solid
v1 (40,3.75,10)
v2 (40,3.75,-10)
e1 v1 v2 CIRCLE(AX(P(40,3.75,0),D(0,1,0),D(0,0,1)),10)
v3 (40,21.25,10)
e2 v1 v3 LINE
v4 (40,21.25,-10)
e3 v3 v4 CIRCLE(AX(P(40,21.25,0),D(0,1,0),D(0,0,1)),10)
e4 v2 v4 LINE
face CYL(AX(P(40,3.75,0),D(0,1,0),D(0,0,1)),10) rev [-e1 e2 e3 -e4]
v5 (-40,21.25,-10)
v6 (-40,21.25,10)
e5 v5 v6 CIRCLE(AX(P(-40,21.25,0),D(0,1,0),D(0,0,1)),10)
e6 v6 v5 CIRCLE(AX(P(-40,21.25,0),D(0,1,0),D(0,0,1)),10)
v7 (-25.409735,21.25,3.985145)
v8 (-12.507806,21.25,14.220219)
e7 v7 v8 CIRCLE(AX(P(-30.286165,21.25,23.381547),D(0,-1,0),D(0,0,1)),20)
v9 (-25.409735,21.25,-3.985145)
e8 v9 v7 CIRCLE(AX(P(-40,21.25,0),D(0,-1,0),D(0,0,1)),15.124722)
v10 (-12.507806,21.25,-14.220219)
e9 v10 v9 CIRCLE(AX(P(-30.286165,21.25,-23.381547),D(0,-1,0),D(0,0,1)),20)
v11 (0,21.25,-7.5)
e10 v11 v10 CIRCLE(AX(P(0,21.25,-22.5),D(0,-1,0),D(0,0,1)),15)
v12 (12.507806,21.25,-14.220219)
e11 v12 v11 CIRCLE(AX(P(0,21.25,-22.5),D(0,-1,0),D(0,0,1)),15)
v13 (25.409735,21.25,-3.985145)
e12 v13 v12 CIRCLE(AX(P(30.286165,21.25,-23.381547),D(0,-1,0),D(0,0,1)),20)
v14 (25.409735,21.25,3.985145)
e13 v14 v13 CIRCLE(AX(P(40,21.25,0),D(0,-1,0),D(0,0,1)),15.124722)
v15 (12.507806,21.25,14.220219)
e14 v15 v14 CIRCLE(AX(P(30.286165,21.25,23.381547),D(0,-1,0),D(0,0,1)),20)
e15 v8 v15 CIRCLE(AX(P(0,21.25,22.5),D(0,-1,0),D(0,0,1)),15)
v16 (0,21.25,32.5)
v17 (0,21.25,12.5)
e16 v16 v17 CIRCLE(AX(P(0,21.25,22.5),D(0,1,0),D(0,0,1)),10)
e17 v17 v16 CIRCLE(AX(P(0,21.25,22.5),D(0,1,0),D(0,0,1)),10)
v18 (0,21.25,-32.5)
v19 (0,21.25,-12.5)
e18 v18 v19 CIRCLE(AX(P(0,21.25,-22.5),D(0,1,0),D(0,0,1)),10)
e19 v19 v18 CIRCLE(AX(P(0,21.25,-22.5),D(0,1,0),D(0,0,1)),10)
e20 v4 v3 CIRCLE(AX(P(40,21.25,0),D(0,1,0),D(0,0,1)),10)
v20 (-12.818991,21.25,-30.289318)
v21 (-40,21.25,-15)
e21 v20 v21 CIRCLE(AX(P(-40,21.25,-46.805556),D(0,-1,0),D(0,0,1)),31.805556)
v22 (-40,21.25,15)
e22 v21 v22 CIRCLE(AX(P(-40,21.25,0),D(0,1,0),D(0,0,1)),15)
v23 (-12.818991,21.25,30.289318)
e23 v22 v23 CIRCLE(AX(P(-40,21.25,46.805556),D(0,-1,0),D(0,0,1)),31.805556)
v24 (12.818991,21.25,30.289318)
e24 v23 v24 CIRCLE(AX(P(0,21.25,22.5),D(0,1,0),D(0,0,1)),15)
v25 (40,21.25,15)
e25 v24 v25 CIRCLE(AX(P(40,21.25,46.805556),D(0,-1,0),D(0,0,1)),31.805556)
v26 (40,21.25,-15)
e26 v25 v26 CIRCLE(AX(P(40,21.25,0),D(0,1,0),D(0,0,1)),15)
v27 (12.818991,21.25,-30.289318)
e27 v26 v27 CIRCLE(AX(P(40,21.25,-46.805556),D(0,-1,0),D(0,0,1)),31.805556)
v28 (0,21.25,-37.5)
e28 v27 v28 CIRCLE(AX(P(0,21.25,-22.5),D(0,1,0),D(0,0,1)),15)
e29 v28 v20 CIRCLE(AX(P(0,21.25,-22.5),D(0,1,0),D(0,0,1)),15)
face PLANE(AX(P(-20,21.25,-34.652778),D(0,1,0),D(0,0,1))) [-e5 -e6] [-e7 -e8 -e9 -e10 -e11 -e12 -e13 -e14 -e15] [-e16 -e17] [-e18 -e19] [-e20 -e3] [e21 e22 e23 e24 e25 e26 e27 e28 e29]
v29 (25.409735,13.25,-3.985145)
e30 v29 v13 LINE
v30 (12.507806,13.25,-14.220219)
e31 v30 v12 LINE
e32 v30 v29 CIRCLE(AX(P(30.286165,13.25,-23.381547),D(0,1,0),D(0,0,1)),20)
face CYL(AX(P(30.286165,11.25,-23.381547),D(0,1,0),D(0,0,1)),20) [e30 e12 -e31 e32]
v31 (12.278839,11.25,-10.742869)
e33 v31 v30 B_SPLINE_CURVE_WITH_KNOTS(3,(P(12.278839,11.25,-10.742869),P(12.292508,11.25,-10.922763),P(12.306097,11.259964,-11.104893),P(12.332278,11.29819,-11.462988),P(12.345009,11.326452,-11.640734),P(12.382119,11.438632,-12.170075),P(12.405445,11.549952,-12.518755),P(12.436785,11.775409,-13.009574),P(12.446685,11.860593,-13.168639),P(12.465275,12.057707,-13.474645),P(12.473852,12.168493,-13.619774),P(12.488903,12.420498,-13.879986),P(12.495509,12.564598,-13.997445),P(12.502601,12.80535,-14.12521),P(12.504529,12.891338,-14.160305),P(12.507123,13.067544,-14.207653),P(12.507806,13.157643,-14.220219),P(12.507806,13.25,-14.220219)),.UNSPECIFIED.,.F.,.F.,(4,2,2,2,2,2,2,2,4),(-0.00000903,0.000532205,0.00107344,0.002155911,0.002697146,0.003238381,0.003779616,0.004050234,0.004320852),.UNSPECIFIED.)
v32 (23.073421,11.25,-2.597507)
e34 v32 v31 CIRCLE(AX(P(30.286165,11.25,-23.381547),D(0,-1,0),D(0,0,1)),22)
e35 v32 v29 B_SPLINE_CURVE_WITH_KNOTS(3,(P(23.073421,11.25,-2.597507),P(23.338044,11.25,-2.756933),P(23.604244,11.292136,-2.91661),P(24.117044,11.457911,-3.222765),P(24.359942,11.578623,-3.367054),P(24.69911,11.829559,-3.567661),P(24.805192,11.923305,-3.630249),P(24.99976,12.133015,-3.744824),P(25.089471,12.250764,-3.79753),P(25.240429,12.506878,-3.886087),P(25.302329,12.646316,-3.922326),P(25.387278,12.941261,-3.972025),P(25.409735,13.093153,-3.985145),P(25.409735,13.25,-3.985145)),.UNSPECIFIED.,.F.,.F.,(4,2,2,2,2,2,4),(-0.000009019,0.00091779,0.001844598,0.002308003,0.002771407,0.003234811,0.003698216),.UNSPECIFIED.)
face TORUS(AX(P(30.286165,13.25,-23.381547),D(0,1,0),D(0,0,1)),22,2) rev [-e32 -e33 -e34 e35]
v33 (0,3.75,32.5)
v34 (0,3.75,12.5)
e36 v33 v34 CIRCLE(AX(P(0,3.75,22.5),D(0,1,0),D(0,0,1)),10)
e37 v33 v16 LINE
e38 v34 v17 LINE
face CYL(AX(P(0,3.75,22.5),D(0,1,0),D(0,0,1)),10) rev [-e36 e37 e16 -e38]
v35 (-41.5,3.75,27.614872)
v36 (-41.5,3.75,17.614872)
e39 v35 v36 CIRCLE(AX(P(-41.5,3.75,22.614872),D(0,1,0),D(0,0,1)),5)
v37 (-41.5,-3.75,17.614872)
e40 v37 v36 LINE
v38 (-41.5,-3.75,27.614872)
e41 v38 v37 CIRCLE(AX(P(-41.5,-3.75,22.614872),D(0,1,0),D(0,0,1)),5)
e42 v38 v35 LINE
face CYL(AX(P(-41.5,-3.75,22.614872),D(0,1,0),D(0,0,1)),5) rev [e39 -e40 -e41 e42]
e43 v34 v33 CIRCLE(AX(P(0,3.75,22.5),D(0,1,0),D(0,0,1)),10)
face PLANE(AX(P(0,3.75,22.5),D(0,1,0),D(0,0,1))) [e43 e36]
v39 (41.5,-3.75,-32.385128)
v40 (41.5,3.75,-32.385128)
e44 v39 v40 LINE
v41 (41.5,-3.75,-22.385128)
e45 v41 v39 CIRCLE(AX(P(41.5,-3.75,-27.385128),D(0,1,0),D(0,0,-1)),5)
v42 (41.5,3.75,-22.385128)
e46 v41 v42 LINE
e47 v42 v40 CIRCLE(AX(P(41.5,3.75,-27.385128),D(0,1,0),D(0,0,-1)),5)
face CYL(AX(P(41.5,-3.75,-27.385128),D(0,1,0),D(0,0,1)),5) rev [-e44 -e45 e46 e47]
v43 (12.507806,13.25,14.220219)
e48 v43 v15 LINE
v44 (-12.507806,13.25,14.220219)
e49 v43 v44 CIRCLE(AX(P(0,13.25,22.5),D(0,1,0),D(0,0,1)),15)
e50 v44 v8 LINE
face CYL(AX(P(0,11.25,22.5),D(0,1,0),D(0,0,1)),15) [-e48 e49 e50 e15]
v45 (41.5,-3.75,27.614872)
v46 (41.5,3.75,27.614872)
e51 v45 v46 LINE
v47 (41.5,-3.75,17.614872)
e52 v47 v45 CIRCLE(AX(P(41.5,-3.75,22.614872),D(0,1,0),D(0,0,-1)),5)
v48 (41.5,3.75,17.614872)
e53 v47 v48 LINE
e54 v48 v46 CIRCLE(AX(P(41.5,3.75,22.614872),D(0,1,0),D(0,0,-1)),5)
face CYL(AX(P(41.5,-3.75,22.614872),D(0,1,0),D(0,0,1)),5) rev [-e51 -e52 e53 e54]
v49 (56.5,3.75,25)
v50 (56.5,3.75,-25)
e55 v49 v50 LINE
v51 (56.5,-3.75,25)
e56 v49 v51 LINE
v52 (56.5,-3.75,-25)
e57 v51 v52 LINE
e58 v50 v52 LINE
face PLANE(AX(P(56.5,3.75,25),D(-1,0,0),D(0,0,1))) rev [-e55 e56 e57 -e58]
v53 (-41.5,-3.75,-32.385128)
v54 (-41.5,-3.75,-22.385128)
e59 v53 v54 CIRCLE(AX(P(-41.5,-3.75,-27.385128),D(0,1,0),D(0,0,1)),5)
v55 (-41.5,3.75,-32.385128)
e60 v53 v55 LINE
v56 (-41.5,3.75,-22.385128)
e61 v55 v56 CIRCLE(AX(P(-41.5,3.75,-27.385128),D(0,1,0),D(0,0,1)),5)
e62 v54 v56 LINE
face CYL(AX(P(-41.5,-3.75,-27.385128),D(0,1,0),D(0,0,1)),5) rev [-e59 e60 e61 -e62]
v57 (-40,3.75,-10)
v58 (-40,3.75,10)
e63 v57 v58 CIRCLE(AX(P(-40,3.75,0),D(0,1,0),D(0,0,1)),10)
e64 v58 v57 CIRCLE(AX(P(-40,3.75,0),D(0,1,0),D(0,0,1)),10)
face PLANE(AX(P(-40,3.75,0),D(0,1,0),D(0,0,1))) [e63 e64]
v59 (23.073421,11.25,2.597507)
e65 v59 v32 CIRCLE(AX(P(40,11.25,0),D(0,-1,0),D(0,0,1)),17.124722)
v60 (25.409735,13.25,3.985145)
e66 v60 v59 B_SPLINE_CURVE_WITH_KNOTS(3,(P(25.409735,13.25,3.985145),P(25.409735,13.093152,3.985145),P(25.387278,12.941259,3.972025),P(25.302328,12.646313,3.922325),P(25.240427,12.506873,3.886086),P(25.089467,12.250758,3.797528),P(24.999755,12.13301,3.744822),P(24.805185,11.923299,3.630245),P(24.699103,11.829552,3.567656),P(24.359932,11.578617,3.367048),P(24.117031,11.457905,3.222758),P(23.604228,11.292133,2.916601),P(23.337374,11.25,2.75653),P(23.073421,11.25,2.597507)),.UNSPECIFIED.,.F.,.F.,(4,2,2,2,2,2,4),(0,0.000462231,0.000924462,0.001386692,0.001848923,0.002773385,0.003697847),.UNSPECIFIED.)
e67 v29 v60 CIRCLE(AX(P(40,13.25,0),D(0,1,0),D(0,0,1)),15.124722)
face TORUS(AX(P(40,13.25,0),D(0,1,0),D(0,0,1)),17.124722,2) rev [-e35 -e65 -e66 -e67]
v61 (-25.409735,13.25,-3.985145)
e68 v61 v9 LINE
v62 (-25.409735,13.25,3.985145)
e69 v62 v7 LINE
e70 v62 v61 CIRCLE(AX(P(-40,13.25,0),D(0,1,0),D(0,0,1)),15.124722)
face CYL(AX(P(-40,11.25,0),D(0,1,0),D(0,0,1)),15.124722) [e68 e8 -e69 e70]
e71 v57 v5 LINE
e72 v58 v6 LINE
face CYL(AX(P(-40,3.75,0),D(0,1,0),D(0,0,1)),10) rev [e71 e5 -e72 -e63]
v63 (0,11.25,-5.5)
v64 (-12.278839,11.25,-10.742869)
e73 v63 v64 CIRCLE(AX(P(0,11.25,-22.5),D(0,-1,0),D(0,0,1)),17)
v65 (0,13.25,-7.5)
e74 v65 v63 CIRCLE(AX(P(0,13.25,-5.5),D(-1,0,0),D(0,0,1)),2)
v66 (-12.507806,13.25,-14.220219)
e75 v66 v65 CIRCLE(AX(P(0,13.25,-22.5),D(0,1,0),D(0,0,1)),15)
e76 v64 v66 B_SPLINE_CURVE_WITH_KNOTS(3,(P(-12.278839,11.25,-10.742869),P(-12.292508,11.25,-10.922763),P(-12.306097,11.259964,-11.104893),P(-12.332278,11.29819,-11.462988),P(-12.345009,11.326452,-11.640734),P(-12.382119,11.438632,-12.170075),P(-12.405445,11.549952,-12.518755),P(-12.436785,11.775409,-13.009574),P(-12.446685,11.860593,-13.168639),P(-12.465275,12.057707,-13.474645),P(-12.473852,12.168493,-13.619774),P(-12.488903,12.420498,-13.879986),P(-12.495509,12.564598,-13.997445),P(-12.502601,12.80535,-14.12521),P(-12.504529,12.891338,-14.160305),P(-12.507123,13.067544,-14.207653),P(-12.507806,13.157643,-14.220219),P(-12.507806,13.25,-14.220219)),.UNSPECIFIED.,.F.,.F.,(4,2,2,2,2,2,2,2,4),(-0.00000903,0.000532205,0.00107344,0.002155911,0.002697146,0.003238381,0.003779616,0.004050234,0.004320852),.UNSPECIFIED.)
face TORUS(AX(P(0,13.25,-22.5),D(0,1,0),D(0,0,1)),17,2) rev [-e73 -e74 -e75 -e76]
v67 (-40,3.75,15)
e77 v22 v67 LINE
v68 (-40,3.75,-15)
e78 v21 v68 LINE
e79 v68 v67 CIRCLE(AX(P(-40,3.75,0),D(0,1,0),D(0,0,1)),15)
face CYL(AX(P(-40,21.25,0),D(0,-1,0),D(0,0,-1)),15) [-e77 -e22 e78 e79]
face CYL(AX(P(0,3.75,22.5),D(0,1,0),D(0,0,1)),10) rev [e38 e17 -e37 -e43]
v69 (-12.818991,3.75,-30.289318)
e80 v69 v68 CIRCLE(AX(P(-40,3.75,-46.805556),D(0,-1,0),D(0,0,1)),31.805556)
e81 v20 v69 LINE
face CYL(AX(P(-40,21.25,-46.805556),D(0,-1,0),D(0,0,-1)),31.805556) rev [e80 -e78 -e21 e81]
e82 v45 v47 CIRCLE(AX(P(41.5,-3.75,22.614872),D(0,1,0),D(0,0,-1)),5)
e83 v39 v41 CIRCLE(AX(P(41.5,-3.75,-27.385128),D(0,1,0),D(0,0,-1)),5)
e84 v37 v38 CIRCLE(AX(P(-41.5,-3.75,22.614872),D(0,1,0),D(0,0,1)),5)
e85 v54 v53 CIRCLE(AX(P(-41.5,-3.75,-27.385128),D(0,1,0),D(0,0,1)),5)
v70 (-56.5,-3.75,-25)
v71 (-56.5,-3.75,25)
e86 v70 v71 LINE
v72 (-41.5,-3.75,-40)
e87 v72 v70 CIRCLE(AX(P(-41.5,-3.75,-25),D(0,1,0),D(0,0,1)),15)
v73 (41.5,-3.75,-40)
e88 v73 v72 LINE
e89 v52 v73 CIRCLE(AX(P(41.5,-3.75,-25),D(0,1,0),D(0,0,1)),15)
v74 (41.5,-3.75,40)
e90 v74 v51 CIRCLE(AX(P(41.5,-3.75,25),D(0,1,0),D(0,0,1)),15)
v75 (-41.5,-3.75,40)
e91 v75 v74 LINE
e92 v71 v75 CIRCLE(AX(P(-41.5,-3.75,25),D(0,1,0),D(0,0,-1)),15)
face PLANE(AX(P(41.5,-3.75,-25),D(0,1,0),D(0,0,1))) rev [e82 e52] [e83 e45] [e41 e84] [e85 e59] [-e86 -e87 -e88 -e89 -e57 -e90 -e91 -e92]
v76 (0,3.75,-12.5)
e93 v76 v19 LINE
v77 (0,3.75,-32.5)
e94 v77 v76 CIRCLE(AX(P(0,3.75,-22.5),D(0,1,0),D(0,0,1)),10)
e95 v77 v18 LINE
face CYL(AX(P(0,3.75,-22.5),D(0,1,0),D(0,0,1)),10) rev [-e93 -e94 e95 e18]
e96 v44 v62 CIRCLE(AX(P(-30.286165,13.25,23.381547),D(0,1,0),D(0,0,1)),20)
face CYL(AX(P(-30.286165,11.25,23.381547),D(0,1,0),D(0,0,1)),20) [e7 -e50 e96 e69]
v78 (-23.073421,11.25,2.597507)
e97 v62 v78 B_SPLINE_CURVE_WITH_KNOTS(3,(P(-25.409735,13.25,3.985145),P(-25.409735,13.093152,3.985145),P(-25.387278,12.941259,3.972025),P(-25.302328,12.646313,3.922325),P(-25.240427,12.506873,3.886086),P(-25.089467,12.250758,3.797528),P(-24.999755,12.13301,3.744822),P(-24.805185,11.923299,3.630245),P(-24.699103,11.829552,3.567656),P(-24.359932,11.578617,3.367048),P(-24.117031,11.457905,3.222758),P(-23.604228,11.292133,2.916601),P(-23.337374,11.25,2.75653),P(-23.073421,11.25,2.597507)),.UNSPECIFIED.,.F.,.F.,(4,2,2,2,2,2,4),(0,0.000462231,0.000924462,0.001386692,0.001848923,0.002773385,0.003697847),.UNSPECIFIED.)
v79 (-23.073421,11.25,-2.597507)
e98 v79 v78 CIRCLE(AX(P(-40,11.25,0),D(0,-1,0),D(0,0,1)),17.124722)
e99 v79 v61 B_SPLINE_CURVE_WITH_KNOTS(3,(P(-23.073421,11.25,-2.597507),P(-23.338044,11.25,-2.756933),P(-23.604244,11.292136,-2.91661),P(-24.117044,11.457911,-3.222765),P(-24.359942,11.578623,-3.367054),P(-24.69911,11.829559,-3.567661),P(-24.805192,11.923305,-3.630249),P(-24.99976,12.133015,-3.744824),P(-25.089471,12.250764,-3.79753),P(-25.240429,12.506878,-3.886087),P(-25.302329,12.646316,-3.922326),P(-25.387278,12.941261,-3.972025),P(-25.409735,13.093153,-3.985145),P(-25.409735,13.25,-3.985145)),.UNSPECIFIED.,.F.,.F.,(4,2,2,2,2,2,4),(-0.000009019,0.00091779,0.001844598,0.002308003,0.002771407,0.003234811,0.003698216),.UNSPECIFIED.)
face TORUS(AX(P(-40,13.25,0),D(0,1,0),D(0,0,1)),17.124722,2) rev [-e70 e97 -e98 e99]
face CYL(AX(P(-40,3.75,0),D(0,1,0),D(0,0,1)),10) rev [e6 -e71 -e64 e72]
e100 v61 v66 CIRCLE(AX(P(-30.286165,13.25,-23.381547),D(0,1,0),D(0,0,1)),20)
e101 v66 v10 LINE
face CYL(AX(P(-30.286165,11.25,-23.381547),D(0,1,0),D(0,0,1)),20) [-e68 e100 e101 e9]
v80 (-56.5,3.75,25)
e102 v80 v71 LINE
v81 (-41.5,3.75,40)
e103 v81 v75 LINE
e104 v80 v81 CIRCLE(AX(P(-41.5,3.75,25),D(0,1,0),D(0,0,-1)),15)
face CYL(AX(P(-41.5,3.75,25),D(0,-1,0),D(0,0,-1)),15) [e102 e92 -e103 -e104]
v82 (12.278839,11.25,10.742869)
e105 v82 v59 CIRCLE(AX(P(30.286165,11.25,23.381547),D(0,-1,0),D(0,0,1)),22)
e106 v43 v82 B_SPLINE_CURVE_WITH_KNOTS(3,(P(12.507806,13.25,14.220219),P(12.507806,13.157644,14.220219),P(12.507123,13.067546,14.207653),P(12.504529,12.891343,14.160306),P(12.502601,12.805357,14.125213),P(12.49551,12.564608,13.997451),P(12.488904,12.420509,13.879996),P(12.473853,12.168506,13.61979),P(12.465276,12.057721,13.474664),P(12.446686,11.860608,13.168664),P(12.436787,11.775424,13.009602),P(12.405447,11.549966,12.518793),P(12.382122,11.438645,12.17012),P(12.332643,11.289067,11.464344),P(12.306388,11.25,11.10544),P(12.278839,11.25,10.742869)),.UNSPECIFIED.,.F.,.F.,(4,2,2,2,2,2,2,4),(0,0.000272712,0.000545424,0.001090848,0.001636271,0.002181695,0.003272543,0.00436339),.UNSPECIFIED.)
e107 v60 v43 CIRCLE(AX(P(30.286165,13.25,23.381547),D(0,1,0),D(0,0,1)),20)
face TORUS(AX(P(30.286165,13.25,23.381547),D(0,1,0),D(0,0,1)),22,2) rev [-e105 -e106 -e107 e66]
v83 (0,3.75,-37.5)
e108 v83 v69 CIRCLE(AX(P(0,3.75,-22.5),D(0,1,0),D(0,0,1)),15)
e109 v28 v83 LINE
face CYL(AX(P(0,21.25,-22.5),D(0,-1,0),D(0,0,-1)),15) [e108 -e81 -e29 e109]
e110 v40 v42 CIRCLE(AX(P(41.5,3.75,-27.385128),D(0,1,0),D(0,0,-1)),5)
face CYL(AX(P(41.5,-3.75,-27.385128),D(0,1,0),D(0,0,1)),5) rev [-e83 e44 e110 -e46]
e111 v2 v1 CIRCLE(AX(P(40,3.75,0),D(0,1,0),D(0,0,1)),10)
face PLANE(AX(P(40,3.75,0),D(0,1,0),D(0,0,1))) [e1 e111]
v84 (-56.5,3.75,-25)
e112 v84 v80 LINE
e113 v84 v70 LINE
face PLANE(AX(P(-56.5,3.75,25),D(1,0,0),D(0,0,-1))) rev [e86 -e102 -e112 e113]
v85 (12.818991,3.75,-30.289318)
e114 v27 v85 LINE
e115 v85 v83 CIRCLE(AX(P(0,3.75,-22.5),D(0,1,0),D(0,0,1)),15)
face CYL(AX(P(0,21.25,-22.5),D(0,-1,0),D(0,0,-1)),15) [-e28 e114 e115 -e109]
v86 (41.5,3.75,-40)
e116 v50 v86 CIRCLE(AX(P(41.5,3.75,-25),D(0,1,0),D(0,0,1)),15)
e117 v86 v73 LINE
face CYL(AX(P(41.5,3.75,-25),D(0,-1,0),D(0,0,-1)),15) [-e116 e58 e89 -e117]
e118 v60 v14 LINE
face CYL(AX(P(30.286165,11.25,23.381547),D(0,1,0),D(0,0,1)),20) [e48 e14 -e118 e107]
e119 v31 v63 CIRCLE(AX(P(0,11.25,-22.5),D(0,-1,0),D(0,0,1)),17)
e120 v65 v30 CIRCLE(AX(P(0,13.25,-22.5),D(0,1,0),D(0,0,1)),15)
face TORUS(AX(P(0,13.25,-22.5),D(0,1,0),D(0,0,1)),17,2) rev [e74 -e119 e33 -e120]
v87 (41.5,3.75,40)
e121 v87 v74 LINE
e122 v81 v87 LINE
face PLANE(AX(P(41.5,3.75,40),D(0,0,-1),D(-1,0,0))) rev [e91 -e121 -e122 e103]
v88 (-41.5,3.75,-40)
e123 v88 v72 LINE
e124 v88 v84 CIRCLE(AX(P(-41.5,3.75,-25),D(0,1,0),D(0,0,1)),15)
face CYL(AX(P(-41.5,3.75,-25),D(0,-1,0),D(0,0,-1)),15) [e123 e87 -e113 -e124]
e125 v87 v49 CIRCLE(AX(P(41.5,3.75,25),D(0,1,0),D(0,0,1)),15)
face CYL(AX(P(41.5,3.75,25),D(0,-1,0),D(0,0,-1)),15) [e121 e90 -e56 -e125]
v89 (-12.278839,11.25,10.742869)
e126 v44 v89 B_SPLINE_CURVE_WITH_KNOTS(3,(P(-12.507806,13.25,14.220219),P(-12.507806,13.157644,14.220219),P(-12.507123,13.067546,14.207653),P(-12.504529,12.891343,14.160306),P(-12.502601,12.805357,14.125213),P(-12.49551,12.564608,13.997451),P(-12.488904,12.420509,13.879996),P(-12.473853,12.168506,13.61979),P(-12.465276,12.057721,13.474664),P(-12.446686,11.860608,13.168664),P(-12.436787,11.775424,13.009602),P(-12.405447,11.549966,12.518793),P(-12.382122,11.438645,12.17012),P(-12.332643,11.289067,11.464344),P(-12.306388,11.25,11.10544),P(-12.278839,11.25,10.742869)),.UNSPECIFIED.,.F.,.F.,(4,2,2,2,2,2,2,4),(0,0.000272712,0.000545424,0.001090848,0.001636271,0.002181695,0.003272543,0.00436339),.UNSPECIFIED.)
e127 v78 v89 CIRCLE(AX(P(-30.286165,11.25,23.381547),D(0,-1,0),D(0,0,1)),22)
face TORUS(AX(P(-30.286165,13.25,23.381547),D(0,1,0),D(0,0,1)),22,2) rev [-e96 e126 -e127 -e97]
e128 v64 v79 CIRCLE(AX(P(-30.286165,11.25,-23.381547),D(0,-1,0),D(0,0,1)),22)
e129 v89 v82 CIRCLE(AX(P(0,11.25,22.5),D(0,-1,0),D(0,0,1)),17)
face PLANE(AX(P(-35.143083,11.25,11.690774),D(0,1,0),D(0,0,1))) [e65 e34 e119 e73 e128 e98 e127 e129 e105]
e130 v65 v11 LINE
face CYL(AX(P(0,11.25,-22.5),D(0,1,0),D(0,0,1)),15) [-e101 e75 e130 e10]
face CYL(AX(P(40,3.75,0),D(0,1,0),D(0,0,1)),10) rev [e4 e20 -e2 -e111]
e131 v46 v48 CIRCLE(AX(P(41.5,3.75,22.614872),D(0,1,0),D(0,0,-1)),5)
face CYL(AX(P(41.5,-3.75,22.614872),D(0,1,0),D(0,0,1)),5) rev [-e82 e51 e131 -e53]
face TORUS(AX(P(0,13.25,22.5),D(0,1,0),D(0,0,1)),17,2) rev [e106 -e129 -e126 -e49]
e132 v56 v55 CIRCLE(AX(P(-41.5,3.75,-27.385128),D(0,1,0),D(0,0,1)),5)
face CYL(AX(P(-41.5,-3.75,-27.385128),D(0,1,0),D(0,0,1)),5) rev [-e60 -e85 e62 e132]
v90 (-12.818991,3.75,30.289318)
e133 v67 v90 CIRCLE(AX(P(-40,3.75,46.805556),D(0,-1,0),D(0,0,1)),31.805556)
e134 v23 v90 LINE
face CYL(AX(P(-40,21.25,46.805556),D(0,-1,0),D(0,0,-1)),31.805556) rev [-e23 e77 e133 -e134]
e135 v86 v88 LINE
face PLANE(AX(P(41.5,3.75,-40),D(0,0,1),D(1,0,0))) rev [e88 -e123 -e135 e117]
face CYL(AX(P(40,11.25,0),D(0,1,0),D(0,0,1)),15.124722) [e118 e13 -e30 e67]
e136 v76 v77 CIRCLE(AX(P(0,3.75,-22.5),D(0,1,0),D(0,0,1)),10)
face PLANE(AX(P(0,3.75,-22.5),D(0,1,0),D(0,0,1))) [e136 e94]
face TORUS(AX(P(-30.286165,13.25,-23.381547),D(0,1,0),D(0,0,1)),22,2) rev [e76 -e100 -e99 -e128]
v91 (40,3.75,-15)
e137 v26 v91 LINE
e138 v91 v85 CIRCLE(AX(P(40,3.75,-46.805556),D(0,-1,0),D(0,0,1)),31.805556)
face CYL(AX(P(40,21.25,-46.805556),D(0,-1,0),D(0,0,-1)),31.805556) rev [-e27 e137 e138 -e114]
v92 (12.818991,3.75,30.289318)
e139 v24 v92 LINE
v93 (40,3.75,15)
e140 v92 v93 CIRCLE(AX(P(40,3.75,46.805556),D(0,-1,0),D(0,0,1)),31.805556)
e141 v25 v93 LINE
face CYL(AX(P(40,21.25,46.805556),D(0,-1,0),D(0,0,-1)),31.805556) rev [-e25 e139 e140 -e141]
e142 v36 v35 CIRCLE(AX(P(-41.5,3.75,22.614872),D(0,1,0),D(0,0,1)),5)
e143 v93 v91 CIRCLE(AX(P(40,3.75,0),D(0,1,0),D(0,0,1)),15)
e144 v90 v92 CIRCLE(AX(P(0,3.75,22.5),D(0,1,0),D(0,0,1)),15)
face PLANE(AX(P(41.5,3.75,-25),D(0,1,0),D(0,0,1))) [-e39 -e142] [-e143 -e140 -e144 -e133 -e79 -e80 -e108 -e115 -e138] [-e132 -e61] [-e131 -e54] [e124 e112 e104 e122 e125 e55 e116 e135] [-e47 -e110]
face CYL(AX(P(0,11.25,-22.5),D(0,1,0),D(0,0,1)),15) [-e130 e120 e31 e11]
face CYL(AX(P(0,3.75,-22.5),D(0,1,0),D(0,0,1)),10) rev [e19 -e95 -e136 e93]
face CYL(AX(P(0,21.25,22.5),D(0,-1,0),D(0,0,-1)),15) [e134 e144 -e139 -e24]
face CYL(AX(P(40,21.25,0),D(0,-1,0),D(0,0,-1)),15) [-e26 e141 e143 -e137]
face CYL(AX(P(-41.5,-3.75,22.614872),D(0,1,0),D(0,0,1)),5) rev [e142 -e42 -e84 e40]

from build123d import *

# Parameters (mm, degrees)
BASE_PLATE_DEPTH           = 3.75
MOUNTING_HOLES_SKETCH_R    = 5
MOUNTING_HOLES_4X_10_DEPTH = 7.5
LOBED_BOSS_DEPTH           = 17.5
STAR_START                 = -10
STAR_POCKET_DEPTH          = 10
BOSS_BORES_SKETCH_R        = 10
BOSS_BORES_4X_DEPTH        = 17.5
POCKET_FILLETS_R2_R        = 2


with BuildPart() as part:
    # Base Plate Profile → Base Plate (new, symmetric)
    with BuildSketch(Plane(origin=(0, 0, 0), x_dir=(1, 0, 0), z_dir=(0, 1, 0))):
        with BuildLine():
            Line((41.5, -40), (-41.5, -40))
            ThreePointArc((-41.5, -40), (-52.106601718, -35.606601718), (-56.5, -25))
            Line((-56.5, -25), (-56.5, 25))
            ThreePointArc((-56.5, 25), (-52.106601718, 35.606601718), (-41.5, 40))
            Line((-41.5, 40), (41.5, 40))
            ThreePointArc((41.5, 40), (52.106601718, 35.606601718), (56.5, 25))
            Line((56.5, 25), (56.5, -25))
            ThreePointArc((56.5, -25), (52.106601718, -35.606601718), (41.5, -40))
        make_face()
    extrude(amount=BASE_PLATE_DEPTH, both=True)

    # Mounting Holes Sketch → Mounting Holes 4xØ10 (cut)
    with BuildSketch(Plane(origin=(0, 3.75, 0), x_dir=(1, 0, 0), z_dir=(0, 1, 0))):
        with Locations(Location((-41.5, 27.385128328, 0), (0, 0, 270))):
            Circle(MOUNTING_HOLES_SKETCH_R)
        with Locations(Location((-41.5, -22.614871672, 0), (0, 0, 270))):
            Circle(MOUNTING_HOLES_SKETCH_R)
        with Locations(Location((41.5, -22.614871672, 0), (0, 0, 90))):
            Circle(MOUNTING_HOLES_SKETCH_R)
        with Locations(Location((41.5, 27.385128328, 0), (0, 0, 90))):
            Circle(MOUNTING_HOLES_SKETCH_R)
    extrude(amount=-MOUNTING_HOLES_4X_10_DEPTH, mode=Mode.SUBTRACT)

    # Lobed Boss Profile → Lobed Boss (add)
    with BuildSketch(Plane(origin=(0, 3.75, 0), x_dir=(1, 0, 0), z_dir=(0, 1, 0))):
        with BuildLine():
            ThreePointArc((-40, 15), (-55, 0), (-40, -15))
            ThreePointArc((-40, -15), (-24.406968906, -19.084611389), (-12.818991098, -30.289317507))
            ThreePointArc((-12.818991098, -30.289317507), (0, -37.5), (12.818991098, -30.289317507))
            ThreePointArc((12.818991098, -30.289317507), (24.406968906, -19.084611389), (40, -15))
            ThreePointArc((40, -15), (55, 0), (40, 15))
            ThreePointArc((40, 15), (24.406968906, 19.084611389), (12.818991098, 30.289317507))
            ThreePointArc((12.818991098, 30.289317507), (0, 37.5), (-12.818991098, 30.289317507))
            ThreePointArc((-12.818991098, 30.289317507), (-24.406968906, 19.084611389), (-40, 15))
        make_face()
    extrude(amount=LOBED_BOSS_DEPTH)

    # Star Pocket Profile → Star Pocket (cut)
    with BuildSketch(Plane(origin=(0, 21.25, 0), x_dir=(1, 0, 0), z_dir=(0, 1, 0)).offset(STAR_START)):
        with BuildLine():
            ThreePointArc((-25.409734785, -3.985145132), (-24.875277829, 0), (-25.409734785, 3.985145132))
            ThreePointArc((-25.409734785, 3.985145132), (-17.85640049, 7.713077773), (-12.507806345, 14.220218576))
            ThreePointArc((-12.507806345, 14.220218576), (0, 7.5), (12.507806345, 14.220218576))
            ThreePointArc((12.507806345, 14.220218576), (17.85640049, 7.713077773), (25.409734785, 3.985145132))
            ThreePointArc((25.409734785, 3.985145132), (24.875277829, 0), (25.409734785, -3.985145132))
            ThreePointArc((25.409734785, -3.985145132), (17.85640049, -7.713077773), (12.507806345, -14.220218576))
            ThreePointArc((12.507806345, -14.220218576), (0, -7.5), (-12.507806345, -14.220218576))
            ThreePointArc((-12.507806345, -14.220218576), (-17.85640049, -7.713077773), (-25.409734785, -3.985145132))
        make_face()
    extrude(amount=STAR_POCKET_DEPTH, mode=Mode.SUBTRACT)

    # Boss Bores Sketch → Boss Bores 4x (cut)
    with BuildSketch(Plane(origin=(0, 21.25, 0), x_dir=(1, 0, 0), z_dir=(0, 1, 0))):
        with Locations(Location((40, 0, 0), (0, 0, 270))):
            Circle(BOSS_BORES_SKETCH_R)
        with Locations(Location((0, -22.5, 0), (0, 0, 270))):
            Circle(BOSS_BORES_SKETCH_R)
        with Locations(Location((0, 22.5, 0), (0, 0, 270))):
            Circle(BOSS_BORES_SKETCH_R)
        with Locations(Location((-40, 0, 0), (0, 0, 270))):
            Circle(BOSS_BORES_SKETCH_R)
    extrude(amount=-BOSS_BORES_4X_DEPTH, mode=Mode.SUBTRACT)

    # Pocket Fillets R2
    pocket_fillets_r2_edges = [part.edges().sort_by_distance(p)[0] for p in [
        (-17.85640049, 11.25, 7.713077773),
        (-24.875277829, 11.25, 0),
        (-17.85640049, 11.25, -7.713077773),
        (0, 11.25, -7.5),
        (17.85640049, 11.25, -7.713077773),
        (24.875277829, 11.25, 0),
        (17.85640049, 11.25, 7.713077773),
        (0, 11.25, 7.5),
    ]]
    fillet(pocket_fillets_r2_edges, radius=POCKET_FILLETS_R2_R)


solid = part.part
